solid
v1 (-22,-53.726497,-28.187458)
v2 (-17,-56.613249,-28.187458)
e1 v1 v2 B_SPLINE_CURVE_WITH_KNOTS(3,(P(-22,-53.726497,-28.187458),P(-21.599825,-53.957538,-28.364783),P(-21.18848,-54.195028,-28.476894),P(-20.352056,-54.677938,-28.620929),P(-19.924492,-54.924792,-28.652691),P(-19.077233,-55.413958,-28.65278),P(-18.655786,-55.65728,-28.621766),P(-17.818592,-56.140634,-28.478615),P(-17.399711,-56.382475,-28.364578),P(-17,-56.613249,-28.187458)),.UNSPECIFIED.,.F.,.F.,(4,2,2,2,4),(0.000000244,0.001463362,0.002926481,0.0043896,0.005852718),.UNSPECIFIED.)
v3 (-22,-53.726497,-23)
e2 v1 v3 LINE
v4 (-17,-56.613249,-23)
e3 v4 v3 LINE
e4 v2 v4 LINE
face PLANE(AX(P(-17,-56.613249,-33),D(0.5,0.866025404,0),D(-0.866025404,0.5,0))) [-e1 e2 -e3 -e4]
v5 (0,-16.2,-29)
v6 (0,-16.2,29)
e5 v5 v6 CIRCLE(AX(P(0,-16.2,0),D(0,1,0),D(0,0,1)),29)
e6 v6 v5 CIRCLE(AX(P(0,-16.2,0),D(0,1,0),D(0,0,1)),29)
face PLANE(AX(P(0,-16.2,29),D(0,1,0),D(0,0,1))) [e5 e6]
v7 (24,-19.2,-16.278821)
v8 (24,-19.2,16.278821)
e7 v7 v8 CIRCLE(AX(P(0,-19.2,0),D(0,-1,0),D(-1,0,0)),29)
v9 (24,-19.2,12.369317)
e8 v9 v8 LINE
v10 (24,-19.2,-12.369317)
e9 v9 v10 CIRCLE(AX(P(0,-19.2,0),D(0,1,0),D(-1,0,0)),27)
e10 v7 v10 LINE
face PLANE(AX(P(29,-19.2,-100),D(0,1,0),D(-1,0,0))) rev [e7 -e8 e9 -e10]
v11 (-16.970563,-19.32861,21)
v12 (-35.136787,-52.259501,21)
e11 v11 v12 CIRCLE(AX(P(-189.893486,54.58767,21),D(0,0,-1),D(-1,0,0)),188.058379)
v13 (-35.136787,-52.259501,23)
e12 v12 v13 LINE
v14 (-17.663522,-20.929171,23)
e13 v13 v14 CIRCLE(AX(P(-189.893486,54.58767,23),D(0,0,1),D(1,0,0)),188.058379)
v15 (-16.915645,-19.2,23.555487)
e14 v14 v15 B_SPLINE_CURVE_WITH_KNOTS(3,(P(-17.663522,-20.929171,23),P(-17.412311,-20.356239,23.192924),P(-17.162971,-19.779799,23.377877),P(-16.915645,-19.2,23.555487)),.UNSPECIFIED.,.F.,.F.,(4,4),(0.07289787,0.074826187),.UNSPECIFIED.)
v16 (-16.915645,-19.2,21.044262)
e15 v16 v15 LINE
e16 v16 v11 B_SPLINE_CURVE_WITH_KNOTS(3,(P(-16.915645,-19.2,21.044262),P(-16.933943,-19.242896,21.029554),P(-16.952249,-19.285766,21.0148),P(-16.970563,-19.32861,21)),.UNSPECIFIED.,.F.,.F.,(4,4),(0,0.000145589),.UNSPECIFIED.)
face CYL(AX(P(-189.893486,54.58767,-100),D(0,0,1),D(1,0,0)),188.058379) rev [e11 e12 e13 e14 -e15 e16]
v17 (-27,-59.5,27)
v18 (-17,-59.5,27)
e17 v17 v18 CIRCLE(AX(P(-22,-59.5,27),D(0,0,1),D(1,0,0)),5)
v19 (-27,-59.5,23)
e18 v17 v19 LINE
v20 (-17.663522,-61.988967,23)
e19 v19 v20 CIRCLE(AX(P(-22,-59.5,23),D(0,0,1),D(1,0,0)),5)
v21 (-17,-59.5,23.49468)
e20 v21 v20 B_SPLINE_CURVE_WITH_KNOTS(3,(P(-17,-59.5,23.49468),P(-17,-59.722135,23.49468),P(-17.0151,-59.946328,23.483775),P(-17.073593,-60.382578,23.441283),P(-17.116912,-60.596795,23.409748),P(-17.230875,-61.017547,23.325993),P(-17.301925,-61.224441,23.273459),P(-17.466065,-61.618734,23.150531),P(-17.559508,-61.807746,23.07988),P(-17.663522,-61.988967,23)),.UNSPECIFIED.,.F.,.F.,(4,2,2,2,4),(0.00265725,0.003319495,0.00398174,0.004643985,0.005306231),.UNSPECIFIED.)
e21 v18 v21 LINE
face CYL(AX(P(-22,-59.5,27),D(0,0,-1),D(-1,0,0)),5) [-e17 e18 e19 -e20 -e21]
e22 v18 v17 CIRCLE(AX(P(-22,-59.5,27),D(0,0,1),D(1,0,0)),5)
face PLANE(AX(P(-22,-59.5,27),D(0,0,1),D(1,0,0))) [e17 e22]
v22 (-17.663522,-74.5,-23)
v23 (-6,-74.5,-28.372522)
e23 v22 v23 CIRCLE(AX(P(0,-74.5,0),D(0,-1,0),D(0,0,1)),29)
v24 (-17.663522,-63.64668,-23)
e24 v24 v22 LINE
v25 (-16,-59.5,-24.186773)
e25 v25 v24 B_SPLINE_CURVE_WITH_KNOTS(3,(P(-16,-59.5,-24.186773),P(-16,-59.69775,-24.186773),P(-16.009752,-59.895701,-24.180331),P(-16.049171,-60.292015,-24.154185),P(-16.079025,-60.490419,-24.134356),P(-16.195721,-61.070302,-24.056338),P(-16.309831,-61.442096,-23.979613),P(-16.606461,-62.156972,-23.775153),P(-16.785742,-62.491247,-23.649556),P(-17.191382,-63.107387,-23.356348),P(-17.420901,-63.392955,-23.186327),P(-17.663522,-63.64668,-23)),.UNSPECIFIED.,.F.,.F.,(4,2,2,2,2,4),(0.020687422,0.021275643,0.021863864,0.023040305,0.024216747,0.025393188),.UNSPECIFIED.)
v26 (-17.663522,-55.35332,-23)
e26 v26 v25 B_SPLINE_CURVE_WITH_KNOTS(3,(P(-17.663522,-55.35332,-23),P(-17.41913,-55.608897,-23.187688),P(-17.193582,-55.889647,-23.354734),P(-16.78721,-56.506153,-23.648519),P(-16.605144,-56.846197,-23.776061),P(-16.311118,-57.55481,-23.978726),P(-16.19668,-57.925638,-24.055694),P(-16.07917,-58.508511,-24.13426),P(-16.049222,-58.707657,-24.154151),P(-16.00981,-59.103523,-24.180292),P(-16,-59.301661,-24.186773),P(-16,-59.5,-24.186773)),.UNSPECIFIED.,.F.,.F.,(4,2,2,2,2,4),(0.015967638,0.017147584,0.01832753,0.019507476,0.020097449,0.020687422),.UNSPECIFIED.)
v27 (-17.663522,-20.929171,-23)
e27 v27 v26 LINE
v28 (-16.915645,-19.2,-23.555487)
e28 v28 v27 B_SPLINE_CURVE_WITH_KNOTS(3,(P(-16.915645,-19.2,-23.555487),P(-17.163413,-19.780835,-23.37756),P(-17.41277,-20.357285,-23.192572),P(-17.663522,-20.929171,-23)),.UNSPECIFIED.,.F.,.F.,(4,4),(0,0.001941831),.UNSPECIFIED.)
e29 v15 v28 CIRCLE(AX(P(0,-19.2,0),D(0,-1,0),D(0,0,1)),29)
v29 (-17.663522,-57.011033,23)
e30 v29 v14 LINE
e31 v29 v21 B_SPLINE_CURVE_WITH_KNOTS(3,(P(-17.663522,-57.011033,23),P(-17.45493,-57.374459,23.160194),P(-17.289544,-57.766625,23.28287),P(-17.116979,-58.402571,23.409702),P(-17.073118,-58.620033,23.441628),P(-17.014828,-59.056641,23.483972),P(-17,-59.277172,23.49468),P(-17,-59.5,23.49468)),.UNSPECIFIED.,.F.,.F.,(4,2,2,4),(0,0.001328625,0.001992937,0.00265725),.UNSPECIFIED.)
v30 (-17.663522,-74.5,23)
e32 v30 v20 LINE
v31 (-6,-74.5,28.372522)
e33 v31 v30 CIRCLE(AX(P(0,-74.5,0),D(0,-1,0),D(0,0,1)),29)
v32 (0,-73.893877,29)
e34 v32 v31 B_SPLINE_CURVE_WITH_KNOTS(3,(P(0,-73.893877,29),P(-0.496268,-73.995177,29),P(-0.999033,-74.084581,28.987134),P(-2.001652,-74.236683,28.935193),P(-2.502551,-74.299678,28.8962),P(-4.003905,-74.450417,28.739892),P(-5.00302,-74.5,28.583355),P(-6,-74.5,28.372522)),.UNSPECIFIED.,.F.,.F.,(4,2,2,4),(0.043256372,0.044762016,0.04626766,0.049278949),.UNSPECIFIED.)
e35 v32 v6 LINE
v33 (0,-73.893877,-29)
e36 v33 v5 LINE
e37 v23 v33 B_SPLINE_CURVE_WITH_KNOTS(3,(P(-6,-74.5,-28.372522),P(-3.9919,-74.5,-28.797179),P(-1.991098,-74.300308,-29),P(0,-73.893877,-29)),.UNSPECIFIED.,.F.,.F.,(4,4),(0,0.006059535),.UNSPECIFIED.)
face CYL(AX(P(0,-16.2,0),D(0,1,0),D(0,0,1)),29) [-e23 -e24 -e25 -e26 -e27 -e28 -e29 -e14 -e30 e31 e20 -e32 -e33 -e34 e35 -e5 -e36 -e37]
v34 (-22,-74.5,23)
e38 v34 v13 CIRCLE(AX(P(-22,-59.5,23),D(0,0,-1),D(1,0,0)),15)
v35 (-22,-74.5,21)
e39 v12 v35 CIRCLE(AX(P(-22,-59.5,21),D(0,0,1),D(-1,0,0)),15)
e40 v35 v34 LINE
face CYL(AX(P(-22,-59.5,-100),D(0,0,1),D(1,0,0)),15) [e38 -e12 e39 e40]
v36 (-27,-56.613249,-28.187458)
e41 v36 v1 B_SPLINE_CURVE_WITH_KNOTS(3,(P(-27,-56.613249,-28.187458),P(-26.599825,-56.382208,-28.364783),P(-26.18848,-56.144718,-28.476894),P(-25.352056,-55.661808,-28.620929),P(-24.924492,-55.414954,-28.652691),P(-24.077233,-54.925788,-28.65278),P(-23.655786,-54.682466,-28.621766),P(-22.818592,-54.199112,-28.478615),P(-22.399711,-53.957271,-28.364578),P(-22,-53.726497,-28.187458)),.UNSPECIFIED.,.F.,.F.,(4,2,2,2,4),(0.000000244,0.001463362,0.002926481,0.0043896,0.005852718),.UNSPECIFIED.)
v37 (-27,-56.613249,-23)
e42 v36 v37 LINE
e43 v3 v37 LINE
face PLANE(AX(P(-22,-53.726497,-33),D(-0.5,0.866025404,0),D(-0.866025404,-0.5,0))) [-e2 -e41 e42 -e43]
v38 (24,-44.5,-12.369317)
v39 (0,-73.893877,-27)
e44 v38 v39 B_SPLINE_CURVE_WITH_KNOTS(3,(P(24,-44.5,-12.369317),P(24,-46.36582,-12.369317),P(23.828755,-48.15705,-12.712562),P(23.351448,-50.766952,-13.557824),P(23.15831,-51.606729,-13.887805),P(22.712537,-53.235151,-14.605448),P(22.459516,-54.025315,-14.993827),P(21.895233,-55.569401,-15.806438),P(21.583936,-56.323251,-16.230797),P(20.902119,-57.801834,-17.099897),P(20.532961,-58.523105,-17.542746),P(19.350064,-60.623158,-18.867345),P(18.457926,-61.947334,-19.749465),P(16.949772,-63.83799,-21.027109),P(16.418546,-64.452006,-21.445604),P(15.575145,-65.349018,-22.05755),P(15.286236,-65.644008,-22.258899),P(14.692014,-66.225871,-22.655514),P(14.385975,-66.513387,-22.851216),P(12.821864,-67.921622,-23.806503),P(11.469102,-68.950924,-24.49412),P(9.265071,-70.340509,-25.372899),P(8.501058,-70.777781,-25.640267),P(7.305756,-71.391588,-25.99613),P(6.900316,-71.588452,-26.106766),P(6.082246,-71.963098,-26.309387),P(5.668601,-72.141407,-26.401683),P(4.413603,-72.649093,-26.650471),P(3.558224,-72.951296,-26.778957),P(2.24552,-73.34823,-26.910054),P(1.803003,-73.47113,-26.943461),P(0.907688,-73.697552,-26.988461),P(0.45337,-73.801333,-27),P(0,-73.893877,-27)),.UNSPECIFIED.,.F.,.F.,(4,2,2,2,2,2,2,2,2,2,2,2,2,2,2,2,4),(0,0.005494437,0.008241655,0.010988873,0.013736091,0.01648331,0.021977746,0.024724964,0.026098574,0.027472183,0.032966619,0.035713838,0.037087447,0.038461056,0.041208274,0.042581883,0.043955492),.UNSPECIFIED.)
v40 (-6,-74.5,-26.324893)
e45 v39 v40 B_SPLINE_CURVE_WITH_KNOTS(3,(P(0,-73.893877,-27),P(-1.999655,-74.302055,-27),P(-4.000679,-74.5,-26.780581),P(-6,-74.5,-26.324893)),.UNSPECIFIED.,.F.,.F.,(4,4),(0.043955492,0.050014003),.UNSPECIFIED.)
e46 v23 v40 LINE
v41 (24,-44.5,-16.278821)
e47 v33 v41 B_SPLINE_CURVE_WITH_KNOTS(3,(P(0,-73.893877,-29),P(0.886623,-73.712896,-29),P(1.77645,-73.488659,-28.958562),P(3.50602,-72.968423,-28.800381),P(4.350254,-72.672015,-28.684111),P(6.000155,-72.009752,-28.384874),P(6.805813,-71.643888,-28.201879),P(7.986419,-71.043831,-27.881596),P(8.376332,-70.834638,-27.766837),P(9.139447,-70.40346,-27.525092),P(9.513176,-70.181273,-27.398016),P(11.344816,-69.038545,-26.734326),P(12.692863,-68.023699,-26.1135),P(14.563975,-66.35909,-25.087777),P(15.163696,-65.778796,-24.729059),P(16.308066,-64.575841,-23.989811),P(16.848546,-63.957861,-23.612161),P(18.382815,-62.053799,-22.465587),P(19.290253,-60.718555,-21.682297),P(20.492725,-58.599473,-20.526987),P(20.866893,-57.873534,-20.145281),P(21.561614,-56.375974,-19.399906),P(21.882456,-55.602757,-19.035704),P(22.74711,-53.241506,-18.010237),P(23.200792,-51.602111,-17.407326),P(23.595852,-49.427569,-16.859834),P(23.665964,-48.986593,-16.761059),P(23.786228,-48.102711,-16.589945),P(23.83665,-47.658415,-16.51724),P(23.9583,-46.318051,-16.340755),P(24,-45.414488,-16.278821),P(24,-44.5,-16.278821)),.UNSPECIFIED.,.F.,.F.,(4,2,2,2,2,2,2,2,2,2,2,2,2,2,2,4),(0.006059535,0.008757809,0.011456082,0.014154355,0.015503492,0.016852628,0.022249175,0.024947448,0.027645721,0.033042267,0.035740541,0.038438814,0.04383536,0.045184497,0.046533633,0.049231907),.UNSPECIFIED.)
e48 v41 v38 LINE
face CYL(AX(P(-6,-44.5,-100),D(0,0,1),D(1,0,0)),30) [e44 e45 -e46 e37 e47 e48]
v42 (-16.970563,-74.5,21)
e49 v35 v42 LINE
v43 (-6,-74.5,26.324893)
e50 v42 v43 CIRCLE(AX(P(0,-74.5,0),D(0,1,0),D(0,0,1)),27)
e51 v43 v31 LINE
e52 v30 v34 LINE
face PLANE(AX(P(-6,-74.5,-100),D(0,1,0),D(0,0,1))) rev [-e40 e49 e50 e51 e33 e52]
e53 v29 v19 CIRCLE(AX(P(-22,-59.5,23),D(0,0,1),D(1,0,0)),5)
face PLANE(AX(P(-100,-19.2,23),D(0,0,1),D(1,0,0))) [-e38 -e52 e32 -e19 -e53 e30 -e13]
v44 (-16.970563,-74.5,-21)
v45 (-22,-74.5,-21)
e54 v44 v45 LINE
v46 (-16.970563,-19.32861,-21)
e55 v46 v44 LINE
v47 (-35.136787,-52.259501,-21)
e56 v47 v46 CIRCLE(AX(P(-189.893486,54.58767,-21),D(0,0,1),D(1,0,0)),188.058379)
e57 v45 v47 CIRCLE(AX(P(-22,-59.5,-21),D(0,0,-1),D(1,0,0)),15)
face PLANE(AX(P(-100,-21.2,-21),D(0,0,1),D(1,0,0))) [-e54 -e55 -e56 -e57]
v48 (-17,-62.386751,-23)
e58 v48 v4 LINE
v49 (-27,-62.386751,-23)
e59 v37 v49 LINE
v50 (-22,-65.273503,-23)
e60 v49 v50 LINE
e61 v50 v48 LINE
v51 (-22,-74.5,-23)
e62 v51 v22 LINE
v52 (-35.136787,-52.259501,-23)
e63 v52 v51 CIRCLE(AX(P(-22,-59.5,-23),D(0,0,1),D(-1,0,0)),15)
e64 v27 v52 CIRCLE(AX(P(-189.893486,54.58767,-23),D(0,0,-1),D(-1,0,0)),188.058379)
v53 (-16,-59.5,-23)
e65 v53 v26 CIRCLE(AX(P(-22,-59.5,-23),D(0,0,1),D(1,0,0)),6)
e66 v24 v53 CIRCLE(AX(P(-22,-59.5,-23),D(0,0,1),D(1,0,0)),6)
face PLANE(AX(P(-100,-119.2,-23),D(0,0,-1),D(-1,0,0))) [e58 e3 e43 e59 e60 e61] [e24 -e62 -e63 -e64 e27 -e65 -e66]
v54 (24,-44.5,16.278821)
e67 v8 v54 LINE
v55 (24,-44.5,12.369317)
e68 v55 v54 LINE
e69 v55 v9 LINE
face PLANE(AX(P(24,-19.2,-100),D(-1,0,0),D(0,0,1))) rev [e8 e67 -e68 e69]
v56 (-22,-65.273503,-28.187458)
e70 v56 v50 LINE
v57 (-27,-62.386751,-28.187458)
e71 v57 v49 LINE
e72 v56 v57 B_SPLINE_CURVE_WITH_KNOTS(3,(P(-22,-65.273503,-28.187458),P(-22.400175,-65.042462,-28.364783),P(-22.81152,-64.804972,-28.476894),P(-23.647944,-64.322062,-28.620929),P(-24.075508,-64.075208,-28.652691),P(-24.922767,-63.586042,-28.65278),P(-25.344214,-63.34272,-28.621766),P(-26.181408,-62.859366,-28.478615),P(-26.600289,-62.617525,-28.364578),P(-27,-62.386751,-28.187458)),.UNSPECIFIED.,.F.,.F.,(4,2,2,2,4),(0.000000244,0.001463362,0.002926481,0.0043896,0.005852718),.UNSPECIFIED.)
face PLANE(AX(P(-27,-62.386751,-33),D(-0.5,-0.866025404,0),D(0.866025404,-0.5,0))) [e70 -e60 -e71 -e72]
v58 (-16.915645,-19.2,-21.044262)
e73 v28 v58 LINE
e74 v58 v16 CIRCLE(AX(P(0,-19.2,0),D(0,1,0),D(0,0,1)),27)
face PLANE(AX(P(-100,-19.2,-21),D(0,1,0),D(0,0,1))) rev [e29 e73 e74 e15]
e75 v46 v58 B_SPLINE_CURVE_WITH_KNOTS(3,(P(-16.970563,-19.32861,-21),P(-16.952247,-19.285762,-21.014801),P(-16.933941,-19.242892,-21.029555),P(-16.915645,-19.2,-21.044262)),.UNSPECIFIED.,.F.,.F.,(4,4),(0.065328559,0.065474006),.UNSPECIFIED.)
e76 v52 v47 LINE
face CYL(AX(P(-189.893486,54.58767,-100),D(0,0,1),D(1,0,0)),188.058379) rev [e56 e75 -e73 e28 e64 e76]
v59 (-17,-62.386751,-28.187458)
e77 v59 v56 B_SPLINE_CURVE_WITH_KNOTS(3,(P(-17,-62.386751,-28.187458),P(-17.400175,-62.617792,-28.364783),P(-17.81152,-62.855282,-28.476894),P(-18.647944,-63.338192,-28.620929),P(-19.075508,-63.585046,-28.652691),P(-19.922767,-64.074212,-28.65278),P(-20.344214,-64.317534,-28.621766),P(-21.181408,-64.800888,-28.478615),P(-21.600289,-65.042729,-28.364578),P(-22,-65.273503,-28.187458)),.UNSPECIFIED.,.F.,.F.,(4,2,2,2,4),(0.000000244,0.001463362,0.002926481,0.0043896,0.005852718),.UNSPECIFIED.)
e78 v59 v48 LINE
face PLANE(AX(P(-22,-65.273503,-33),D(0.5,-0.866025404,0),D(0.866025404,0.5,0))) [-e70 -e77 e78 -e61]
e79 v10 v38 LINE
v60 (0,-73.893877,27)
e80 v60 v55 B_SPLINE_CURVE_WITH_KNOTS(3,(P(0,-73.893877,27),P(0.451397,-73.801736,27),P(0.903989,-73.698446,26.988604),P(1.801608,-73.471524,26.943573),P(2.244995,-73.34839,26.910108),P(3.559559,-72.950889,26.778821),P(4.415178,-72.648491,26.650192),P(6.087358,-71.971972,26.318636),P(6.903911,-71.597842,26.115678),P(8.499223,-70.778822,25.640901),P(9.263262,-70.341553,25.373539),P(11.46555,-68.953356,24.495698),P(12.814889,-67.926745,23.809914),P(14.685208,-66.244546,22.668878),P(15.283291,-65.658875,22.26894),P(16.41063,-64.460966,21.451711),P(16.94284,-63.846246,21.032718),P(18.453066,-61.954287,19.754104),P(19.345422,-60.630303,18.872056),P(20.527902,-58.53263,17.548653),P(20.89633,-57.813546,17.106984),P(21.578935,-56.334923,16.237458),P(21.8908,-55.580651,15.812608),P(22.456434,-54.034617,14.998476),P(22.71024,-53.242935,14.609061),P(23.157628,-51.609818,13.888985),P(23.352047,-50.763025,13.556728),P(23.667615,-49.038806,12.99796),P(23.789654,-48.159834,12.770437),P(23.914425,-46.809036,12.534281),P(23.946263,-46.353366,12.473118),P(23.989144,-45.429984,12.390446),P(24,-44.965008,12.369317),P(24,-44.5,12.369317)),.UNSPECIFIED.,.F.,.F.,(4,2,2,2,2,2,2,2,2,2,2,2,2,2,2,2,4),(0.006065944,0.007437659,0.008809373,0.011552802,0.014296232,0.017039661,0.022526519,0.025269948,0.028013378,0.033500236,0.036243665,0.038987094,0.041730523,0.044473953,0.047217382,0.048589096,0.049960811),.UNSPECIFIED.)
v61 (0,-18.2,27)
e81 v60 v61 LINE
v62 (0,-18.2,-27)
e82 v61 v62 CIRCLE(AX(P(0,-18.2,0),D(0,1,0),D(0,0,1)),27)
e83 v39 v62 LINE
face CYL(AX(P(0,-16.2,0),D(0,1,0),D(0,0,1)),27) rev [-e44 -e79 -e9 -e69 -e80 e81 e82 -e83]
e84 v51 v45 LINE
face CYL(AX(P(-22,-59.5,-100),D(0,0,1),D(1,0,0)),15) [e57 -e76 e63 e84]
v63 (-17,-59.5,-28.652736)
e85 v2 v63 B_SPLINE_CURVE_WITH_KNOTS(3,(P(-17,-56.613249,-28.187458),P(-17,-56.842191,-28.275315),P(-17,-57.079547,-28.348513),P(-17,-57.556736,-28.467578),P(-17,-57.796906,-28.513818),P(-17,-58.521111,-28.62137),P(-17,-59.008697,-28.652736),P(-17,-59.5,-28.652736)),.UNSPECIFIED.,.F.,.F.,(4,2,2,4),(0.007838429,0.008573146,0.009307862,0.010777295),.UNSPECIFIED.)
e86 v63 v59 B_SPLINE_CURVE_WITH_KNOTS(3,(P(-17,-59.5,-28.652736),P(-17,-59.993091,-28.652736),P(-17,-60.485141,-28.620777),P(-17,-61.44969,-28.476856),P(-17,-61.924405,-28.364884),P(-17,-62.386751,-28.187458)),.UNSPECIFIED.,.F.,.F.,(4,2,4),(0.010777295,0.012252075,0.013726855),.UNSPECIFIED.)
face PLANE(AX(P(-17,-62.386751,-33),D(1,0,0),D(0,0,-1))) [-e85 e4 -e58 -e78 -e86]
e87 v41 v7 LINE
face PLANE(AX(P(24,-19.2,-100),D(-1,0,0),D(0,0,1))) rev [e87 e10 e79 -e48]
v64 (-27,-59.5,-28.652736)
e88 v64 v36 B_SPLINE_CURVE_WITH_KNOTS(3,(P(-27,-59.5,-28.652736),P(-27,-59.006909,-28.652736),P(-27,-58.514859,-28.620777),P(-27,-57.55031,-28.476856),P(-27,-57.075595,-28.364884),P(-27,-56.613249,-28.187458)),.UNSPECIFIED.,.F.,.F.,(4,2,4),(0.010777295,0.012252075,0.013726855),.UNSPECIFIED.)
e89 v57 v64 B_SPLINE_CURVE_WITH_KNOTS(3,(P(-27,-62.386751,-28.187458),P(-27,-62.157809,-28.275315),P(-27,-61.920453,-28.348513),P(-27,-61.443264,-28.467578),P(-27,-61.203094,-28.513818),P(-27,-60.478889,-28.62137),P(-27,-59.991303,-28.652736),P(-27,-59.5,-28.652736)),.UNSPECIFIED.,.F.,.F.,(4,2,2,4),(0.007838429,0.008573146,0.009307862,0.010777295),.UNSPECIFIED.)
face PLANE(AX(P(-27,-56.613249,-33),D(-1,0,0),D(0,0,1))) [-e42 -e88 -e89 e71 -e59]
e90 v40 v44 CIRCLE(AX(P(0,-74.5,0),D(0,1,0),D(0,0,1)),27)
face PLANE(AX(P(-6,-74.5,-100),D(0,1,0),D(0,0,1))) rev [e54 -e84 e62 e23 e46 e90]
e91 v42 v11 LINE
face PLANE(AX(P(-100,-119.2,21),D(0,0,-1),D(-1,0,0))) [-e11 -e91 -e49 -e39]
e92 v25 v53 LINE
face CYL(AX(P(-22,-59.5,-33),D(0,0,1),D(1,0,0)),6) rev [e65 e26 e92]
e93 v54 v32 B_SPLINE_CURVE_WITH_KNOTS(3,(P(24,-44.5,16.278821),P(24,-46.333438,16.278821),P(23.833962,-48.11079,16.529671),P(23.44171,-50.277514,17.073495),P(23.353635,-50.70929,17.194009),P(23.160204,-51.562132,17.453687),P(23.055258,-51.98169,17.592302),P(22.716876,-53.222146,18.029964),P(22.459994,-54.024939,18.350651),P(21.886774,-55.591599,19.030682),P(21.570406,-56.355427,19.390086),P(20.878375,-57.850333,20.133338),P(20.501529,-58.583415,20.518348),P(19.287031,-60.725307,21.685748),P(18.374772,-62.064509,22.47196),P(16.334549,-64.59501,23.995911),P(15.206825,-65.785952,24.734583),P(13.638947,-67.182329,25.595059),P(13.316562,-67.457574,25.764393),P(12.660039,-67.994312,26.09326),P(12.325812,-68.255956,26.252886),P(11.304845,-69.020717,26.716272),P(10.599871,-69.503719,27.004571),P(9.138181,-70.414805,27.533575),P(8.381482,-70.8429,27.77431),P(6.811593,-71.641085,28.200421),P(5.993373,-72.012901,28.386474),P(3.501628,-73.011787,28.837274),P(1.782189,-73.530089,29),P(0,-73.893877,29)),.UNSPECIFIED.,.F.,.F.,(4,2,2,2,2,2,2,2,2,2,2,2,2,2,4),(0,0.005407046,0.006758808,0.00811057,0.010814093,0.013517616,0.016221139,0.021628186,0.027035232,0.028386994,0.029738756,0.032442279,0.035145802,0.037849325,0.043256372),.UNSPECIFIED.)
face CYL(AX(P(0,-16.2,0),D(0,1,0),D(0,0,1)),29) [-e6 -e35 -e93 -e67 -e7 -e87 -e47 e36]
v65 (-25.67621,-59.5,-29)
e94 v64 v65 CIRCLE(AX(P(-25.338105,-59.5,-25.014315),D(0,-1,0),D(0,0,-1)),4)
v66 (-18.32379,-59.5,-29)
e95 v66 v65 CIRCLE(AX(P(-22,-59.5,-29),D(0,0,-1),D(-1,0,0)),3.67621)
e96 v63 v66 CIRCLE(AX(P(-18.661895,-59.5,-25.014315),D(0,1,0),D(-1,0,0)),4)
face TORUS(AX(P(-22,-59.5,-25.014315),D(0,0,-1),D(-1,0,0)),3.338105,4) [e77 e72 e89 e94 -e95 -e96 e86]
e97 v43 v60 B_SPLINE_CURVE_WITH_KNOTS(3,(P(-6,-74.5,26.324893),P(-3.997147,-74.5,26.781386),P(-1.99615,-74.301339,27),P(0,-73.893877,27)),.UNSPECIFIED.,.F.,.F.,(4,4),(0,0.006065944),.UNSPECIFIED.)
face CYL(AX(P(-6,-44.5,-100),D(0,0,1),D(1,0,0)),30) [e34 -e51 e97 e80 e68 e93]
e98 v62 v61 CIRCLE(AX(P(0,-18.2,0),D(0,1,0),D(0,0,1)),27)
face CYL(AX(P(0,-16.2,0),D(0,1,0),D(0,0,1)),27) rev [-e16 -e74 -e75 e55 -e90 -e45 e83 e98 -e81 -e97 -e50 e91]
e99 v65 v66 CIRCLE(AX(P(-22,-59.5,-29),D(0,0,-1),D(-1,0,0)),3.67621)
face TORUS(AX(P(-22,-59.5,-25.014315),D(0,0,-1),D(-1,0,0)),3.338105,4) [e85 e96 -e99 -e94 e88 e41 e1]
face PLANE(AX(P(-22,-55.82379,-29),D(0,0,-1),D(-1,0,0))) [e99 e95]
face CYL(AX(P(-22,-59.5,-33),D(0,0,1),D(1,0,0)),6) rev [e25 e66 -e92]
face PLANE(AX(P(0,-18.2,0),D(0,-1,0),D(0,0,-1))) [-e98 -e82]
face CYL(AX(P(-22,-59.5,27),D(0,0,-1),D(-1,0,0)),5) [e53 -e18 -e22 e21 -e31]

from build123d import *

# Parameters (mm, degrees)
EXTRUDE_1_DEPTH          = 100
SKETCH_3_W               = 42
SKETCH_3_H               = 100
CUT_EXTRUDE_1_DEPTH      = 100
CUT_EXTRUDE_START        = -100
SKETCH_4_R               = 27
CUT_EXTRUDE_2_DEPTH      = 100
CUT_EXTRUDE_3_DEPTH      = 100
CUT_EXTRUDE_3_DEPTH_BACK = 100
SKETCH_6_R               = 5
EXTRUDE_2_DEPTH          = 4
CUT_EXTRUDE_START_2      = -10
SKETCH_8_R               = 6
CUT_EXTRUDE_4_DEPTH      = 10


with BuildPart() as part:
    # 草图1 → 旋转1 (revolve)
    with BuildSketch(Plane(origin=(0, 0, 0), x_dir=(0, 0, -1), z_dir=(1, 0, 0))):
        Polygon((0, -18.2), (-27, -18.2), (-27, -116.2), (-29, -116.2), (-29, -16.2), (0, -16.2), align=None)
    revolve(axis=Axis((0, -16.2, 0), (0, -1, 0)))

    # 草图2 → 凸台-拉伸1 (add)
    with BuildSketch(Plane(origin=(0, 0, 0), x_dir=(0, 0, -1), z_dir=(1, 0, 0))):
        Polygon((-23, -19.2), (-23, -119.2), (-21, -119.2), (-21, -21.2), (21, -21.2), (21, -119.2), (23, -119.2), (23, -19.2), align=None)
    extrude(amount=-EXTRUDE_1_DEPTH)

    # 草图3 → 切除-拉伸1 (cut)
    with BuildSketch(Plane(origin=(0, 0, 0), x_dir=(0, 0, -1), z_dir=(1, 0, 0))):
        with Locations((0, -69.2)):
            Rectangle(SKETCH_3_W, SKETCH_3_H)
    extrude(amount=-CUT_EXTRUDE_1_DEPTH, mode=Mode.SUBTRACT)

    # 草图4 → 切除-拉伸2 (cut)
    with BuildSketch(Plane(origin=(0, -18.2, 0), x_dir=(1, 0, 0), z_dir=(0, 1, 0)).offset(CUT_EXTRUDE_START)):
        with Locations(Location((0, 0, 0), (0, 0, 270))):
            Circle(SKETCH_4_R)
    extrude(amount=CUT_EXTRUDE_2_DEPTH, mode=Mode.SUBTRACT)

    # 草图5 → 切除-拉伸3 (cut, two sides: drawn at the far end of the back side and taken through both)
    with BuildSketch(Plane.XY.offset(-CUT_EXTRUDE_3_DEPTH_BACK)):
        with BuildLine():
            Line((-120, -19.2), (-120, -120))
            Line((-120, -120), (29, -120))
            Line((29, -120), (29, -19.2))
            Line((29, -19.2), (24, -19.2))
            Line((24, -19.2), (24, -44.5))
            ThreePointArc((24, -44.5), (15.213203436, -65.713203436), (-6, -74.5))
            Line((-6, -74.5), (-22, -74.5))
            ThreePointArc((-22, -74.5), (-34.915252207, -67.128647352), (-35.136787274, -52.25950139))
            ThreePointArc((-35.136787274, -52.25950139), (-25.194624928, -36.188092129), (-16.915644702, -19.2))
            Line((-16.915644702, -19.2), (-120, -19.2))
        make_face()
    extrude(amount=CUT_EXTRUDE_3_DEPTH + CUT_EXTRUDE_3_DEPTH_BACK, mode=Mode.SUBTRACT)

    # 草图6 → 凸台-拉伸2 (add)
    with BuildSketch(Plane.XY.offset(23)):
        with Locations(Location((-22, -59.5, 0), (0, 0, 29.854118281))):
            Circle(SKETCH_6_R)
    extrude(amount=EXTRUDE_2_DEPTH)

    # 草图7 → 旋转2 (revolve)
    with BuildSketch(Plane(origin=(-22, 0, 0), x_dir=(0, 0, -1), z_dir=(1, 0, 0)), mode=Mode.PRIVATE) as revolve_2_sk:
        with BuildLine():
            Line((23, -59.5), (23, -53.5))
            Line((23, -53.5), (28, -53.5))
            ThreePointArc((28, -53.5), (28.688549603, -54.580756174), (29, -55.823790008))
            Line((29, -55.823790008), (29, -59.5))
            Line((29, -59.5), (23, -59.5))
        make_face()
    revolve(revolve_2_sk.sketch.rotate(Axis((-22, -59.5, -29), (0, 0, 1)), 90), axis=Axis((-22, -59.5, -29), (0, 0, 1)))

    # 草图8 → 切除-拉伸4 (cut)
    with BuildSketch(Plane.XY.offset(-23).offset(CUT_EXTRUDE_START_2)):
        with Locations((-22, -59.5)):
            Circle(SKETCH_8_R)
        Polygon((-27, -56.613248654), (-27, -62.386751346), (-22, -65.273502692), (-17, -62.386751346), (-17, -56.613248654), (-22, -53.726497308), align=None, mode=Mode.SUBTRACT)
    extrude(amount=CUT_EXTRUDE_4_DEPTH, mode=Mode.SUBTRACT)


solid = part.part
